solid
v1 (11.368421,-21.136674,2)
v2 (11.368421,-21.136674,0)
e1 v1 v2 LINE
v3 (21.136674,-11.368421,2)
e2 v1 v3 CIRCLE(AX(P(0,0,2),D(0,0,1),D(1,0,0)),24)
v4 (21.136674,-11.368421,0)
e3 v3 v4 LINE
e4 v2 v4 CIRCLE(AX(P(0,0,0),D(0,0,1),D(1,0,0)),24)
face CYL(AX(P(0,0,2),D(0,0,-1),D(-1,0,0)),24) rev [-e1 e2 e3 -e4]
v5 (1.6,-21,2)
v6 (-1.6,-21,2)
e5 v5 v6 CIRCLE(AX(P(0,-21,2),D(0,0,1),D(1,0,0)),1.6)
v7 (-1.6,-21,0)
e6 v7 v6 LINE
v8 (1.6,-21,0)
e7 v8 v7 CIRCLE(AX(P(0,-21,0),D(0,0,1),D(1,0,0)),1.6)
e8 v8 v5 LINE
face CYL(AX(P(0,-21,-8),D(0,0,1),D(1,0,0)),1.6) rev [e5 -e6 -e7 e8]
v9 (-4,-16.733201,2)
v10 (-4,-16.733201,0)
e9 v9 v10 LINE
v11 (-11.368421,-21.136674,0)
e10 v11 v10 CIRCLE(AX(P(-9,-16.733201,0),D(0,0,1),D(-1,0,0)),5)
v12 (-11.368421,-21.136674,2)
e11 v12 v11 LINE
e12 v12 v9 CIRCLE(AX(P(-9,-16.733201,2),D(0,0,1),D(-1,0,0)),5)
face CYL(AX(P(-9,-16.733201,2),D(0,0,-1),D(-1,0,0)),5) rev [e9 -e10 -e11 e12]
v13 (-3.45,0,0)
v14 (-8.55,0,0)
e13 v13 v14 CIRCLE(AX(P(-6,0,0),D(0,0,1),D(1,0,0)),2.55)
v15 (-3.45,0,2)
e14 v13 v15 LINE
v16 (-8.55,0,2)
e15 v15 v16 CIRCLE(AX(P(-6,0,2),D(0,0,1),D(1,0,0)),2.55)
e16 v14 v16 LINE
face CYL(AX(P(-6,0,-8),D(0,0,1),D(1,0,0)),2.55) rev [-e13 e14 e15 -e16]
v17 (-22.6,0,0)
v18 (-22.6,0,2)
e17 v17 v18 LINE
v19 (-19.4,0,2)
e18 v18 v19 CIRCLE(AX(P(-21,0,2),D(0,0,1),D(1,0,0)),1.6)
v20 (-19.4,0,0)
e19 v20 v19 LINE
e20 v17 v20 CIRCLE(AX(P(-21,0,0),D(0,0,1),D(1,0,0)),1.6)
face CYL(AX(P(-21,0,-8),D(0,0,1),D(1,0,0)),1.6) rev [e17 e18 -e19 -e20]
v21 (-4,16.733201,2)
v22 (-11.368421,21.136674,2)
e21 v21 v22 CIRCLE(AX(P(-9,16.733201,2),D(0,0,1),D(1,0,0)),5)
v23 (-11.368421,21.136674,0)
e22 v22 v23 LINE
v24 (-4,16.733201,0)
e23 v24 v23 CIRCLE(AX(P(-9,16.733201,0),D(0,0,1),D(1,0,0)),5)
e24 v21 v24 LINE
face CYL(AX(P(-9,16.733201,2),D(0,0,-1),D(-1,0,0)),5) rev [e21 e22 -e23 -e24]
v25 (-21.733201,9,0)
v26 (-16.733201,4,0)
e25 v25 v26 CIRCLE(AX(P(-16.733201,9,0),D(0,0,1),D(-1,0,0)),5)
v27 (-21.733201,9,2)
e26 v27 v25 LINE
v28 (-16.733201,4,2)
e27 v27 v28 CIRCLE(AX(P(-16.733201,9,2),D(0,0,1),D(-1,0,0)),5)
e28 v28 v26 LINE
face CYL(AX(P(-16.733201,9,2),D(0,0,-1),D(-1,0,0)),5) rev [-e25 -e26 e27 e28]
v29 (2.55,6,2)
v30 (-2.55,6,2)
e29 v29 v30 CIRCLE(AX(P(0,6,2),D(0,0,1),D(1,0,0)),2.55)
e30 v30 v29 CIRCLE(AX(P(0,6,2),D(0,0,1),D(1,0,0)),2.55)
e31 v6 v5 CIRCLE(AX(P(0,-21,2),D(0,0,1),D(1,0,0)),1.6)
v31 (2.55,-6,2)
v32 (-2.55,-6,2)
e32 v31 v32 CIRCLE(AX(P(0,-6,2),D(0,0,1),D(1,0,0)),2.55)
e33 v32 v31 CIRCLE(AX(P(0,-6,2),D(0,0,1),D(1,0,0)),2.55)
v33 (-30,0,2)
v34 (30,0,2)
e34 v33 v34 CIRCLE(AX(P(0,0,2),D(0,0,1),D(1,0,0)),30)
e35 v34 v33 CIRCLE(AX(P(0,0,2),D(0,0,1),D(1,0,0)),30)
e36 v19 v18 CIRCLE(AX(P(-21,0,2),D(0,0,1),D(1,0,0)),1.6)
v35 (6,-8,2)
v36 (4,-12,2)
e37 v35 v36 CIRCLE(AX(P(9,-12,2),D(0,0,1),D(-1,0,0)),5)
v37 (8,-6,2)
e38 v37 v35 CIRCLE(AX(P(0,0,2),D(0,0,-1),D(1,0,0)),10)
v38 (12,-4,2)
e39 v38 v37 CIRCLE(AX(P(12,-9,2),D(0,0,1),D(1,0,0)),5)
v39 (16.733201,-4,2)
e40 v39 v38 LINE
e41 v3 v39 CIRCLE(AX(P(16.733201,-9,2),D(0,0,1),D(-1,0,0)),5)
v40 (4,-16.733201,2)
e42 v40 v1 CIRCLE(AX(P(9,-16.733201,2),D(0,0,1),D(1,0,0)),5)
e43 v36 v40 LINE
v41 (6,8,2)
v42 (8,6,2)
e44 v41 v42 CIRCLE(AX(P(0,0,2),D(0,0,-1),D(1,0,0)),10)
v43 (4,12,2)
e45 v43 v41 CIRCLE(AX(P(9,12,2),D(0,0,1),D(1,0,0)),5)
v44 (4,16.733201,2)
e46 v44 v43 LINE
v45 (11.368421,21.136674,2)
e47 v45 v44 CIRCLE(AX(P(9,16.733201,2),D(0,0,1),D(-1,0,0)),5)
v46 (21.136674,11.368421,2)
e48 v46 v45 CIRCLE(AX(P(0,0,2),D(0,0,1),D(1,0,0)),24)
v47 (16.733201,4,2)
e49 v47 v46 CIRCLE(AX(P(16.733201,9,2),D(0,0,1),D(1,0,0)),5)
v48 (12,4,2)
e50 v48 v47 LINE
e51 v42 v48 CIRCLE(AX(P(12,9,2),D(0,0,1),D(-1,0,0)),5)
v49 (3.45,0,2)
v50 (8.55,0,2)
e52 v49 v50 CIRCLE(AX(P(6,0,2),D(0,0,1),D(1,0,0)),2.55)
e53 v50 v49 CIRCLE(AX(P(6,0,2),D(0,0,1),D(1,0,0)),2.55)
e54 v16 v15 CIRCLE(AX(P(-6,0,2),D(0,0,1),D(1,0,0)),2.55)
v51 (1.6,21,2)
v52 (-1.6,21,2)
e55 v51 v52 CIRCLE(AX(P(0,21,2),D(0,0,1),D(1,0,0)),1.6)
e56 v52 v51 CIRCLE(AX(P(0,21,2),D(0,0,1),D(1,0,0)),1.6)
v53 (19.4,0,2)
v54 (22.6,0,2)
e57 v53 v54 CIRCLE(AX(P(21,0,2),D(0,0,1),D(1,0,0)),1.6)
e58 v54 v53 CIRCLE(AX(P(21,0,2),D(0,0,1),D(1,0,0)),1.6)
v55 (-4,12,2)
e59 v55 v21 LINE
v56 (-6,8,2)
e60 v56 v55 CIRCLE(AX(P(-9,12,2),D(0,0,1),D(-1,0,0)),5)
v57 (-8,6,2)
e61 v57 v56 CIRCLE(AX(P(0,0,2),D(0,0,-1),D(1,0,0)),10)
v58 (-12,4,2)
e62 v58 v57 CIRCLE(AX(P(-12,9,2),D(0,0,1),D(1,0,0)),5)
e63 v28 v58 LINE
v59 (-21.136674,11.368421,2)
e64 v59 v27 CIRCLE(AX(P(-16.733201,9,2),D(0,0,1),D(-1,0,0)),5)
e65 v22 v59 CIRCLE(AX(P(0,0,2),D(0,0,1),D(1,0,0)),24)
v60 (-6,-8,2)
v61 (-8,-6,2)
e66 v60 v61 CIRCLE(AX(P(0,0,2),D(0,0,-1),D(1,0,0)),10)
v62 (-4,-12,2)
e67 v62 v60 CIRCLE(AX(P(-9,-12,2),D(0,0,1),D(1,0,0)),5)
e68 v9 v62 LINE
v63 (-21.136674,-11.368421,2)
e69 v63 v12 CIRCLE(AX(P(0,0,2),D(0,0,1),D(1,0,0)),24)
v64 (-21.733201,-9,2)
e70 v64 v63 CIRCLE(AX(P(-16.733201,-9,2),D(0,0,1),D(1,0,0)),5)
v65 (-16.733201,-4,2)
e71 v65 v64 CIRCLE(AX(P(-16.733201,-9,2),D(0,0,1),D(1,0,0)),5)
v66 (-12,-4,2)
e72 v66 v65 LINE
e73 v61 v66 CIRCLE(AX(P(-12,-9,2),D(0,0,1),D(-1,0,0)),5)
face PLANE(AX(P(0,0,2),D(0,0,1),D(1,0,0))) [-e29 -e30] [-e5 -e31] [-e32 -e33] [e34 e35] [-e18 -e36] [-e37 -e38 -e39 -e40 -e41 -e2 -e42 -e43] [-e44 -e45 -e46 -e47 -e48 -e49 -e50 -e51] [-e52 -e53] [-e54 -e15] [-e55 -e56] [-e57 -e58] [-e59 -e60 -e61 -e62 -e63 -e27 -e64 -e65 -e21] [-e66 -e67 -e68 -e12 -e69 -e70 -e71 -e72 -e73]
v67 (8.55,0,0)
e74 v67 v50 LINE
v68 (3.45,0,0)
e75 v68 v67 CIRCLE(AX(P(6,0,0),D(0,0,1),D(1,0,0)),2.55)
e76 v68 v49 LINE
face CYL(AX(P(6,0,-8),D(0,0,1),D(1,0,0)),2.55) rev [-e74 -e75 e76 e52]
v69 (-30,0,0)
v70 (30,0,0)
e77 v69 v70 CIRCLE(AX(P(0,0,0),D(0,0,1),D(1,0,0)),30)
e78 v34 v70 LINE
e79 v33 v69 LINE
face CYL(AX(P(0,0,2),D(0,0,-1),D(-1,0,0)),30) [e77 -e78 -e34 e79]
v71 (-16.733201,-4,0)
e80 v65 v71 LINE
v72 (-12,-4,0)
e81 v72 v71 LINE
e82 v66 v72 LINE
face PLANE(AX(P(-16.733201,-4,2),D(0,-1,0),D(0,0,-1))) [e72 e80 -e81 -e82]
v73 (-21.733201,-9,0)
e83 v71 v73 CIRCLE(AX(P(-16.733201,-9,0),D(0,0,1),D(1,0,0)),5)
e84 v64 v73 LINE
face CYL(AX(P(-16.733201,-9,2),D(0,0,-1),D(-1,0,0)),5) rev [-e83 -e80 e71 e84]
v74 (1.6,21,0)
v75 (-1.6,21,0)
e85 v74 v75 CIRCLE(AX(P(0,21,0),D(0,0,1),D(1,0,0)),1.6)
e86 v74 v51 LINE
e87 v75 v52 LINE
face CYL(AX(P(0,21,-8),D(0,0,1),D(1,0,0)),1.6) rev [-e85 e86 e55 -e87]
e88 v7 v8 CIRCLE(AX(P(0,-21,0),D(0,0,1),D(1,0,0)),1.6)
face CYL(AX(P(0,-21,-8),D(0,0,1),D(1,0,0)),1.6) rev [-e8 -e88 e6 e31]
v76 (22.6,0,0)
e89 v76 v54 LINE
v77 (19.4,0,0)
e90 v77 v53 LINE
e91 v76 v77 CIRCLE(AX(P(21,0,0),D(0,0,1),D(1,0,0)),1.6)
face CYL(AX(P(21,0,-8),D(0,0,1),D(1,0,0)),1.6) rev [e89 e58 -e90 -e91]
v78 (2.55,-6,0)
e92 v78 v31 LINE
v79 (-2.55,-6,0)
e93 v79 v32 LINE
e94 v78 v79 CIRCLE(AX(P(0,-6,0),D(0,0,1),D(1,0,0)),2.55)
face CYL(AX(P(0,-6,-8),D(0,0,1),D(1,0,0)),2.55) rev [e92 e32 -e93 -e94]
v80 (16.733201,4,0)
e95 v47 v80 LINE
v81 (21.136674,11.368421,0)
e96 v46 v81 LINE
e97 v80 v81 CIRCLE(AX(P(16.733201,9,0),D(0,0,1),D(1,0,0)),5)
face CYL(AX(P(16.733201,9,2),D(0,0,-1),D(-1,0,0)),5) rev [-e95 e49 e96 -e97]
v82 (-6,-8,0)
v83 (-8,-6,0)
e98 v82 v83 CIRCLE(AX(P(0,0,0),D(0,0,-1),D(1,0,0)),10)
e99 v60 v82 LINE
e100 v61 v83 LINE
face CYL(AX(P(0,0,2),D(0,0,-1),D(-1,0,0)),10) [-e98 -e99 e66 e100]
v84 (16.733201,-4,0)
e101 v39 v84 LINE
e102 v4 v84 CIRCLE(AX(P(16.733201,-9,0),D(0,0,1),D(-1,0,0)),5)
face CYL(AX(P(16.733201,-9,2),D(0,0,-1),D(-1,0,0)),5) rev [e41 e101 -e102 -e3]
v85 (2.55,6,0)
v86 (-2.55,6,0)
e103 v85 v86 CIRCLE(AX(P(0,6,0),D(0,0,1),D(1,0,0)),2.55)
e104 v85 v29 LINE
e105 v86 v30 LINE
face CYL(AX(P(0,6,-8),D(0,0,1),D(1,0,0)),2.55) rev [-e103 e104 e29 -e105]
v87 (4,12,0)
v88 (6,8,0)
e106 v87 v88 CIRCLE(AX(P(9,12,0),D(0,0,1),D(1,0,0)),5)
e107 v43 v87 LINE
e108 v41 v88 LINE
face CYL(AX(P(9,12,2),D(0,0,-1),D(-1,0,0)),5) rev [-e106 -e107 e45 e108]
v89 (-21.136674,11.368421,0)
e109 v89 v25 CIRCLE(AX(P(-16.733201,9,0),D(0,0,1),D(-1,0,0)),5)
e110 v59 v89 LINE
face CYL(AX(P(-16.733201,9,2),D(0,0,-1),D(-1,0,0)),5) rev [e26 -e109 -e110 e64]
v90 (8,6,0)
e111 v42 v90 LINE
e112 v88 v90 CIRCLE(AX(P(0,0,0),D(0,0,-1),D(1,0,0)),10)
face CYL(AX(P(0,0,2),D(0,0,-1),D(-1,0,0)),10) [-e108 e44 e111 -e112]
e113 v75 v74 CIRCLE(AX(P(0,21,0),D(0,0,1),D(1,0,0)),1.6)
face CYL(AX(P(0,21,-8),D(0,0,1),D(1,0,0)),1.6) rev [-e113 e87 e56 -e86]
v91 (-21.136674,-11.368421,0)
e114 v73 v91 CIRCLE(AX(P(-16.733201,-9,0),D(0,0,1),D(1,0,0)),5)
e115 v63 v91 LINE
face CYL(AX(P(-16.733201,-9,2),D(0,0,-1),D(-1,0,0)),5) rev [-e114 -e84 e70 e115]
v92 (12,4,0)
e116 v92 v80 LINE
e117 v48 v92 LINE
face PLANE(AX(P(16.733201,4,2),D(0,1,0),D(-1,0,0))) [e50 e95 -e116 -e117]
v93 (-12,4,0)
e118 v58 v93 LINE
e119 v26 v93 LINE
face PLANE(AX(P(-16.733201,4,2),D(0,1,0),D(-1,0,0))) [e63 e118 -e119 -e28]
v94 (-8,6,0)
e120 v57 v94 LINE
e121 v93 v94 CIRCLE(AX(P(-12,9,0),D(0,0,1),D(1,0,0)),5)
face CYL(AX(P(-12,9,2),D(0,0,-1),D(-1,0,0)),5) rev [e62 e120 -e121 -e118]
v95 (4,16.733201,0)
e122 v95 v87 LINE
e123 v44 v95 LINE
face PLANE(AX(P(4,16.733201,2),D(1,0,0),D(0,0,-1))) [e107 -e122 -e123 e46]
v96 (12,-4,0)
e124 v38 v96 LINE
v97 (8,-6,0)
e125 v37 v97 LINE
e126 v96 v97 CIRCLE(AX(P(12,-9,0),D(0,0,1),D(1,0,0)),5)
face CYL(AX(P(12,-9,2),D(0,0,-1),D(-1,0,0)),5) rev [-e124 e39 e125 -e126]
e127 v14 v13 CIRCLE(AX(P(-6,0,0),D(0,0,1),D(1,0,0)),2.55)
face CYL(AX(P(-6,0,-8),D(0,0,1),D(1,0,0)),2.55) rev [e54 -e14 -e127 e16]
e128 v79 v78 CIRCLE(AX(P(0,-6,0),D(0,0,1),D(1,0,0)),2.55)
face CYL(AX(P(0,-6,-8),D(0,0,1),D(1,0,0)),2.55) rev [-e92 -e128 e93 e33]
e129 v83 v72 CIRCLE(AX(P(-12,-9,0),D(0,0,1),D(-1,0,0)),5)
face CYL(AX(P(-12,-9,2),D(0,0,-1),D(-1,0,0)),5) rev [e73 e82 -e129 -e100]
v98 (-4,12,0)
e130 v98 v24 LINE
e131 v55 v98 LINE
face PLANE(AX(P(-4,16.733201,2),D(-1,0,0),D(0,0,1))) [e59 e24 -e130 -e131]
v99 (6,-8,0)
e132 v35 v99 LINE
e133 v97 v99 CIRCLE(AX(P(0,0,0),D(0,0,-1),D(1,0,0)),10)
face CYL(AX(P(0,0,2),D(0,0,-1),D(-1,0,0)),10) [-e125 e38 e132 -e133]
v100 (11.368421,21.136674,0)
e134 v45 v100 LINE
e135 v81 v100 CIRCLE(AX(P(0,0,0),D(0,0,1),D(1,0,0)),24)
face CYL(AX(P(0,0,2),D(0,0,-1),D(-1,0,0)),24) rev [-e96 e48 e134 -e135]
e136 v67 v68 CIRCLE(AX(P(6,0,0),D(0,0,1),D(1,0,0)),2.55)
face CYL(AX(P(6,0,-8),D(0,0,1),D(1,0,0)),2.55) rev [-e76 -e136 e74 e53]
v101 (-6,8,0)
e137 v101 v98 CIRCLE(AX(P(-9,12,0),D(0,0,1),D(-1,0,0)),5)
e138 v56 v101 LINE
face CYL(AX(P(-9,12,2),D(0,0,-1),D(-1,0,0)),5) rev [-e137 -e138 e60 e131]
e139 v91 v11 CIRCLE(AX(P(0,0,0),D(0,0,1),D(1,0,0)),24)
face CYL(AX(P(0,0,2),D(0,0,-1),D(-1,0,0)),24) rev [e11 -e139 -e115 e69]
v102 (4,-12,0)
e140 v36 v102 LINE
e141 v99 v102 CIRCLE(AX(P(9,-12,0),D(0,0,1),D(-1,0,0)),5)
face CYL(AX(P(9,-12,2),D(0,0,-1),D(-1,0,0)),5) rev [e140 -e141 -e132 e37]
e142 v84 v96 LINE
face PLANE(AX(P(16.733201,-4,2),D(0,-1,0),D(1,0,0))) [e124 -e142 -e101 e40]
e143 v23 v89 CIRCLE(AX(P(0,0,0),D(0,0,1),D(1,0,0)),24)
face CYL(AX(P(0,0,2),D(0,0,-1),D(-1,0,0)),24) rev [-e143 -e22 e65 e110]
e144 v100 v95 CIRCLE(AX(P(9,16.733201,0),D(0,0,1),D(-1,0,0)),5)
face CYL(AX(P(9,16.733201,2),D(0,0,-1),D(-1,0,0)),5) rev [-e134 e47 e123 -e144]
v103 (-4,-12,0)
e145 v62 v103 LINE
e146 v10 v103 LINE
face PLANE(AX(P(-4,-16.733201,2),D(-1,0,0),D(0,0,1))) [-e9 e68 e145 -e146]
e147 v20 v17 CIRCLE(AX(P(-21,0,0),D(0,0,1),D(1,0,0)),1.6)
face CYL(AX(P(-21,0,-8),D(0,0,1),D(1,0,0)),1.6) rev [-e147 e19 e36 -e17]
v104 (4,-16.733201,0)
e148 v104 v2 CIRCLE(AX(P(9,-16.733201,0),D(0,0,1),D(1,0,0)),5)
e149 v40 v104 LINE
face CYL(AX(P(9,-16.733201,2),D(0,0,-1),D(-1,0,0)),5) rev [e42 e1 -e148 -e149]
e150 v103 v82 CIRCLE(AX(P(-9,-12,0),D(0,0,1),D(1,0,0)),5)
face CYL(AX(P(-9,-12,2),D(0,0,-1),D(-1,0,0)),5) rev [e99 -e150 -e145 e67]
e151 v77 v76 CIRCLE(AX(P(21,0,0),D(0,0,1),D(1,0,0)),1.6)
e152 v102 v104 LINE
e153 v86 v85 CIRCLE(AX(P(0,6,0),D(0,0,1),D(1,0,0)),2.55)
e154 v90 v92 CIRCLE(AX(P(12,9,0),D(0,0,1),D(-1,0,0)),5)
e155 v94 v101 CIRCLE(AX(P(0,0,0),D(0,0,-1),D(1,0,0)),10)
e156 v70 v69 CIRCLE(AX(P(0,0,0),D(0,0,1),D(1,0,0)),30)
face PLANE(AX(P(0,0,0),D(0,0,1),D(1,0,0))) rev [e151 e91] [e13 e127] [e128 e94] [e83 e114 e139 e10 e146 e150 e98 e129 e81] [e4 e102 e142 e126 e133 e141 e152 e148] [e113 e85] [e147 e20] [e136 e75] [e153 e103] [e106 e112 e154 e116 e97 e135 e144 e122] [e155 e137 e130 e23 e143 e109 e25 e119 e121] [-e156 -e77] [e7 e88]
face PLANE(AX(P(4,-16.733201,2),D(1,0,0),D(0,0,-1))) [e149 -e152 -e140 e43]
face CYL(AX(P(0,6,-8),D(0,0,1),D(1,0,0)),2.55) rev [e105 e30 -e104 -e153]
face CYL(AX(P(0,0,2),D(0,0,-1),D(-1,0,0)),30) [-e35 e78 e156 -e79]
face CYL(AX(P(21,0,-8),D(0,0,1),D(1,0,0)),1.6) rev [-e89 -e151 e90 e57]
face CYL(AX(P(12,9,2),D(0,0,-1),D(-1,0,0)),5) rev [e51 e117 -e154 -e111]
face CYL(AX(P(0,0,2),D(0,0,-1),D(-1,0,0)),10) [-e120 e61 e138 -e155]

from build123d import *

# Parameters (mm, degrees)
SKETCH_1_R          = 30
EXTRUDE_1_DEPTH     = 2
SKETCH_2_R          = 1.6
CUT_EXTRUDE_1_DEPTH = 10
SKETCH_3_R          = 2.55
CUT_EXTRUDE_2_DEPTH = 10


with BuildPart() as part:
    # 草图1 → 凸台-拉伸1 (new body)
    with BuildSketch(Plane.XY):
        Circle(SKETCH_1_R)
        with BuildLine():
            Line((4, 16.733200531), (4, 12))
            ThreePointArc((4, 12), (4.527864045, 9.763932023), (6, 8))
            ThreePointArc((6, 8), (7.071067812, 7.071067812), (8, 6))
            ThreePointArc((8, 6), (9.763932023, 4.527864045), (12, 4))
            Line((12, 4), (16.733200531, 4))
            ThreePointArc((16.733200531, 4), (21.025175907, 6.43505412), (21.136674355, 11.368421053))
            ThreePointArc((21.136674355, 11.368421053), (16.970562748, 16.970562748), (11.368421053, 21.136674355))
            ThreePointArc((11.368421053, 21.136674355), (6.43505412, 21.025175907), (4, 16.733200531))
        make_face(mode=Mode.SUBTRACT)
        with BuildLine():
            Line((-4, 16.733200531), (-4, 12))
            ThreePointArc((-4, 12), (-4.527864045, 9.763932023), (-6, 8))
            ThreePointArc((-6, 8), (-7.071067812, 7.071067812), (-8, 6))
            ThreePointArc((-8, 6), (-9.763932023, 4.527864045), (-12, 4))
            Line((-12, 4), (-16.733200531, 4))
            ThreePointArc((-16.733200531, 4), (-21.025175907, 6.43505412), (-21.136674355, 11.368421053))
            ThreePointArc((-21.136674355, 11.368421053), (-16.970562748, 16.970562748), (-11.368421053, 21.136674355))
            ThreePointArc((-11.368421053, 21.136674355), (-6.43505412, 21.025175907), (-4, 16.733200531))
        make_face(mode=Mode.SUBTRACT)
        with BuildLine():
            Line((16.733200531, -4), (12, -4))
            ThreePointArc((12, -4), (9.763932023, -4.527864045), (8, -6))
            ThreePointArc((8, -6), (7.071067812, -7.071067812), (6, -8))
            ThreePointArc((6, -8), (4.527864045, -9.763932023), (4, -12))
            Line((4, -12), (4, -16.733200531))
            ThreePointArc((4, -16.733200531), (6.43505412, -21.025175907), (11.368421053, -21.136674355))
            ThreePointArc((11.368421053, -21.136674355), (16.970562748, -16.970562748), (21.136674355, -11.368421053))
            ThreePointArc((21.136674355, -11.368421053), (21.025175907, -6.43505412), (16.733200531, -4))
        make_face(mode=Mode.SUBTRACT)
        with BuildLine():
            Line((-4, -16.733200531), (-4, -12))
            ThreePointArc((-4, -12), (-4.527864045, -9.763932023), (-6, -8))
            ThreePointArc((-6, -8), (-7.071067812, -7.071067812), (-8, -6))
            ThreePointArc((-8, -6), (-9.763932023, -4.527864045), (-12, -4))
            Line((-12, -4), (-16.733200531, -4))
            ThreePointArc((-16.733200531, -4), (-21.025175907, -6.43505412), (-21.136674355, -11.368421053))
            ThreePointArc((-21.136674355, -11.368421053), (-16.970562748, -16.970562748), (-11.368421053, -21.136674355))
            ThreePointArc((-11.368421053, -21.136674355), (-6.43505412, -21.025175907), (-4, -16.733200531))
        make_face(mode=Mode.SUBTRACT)
    extrude(amount=EXTRUDE_1_DEPTH)

    # 草图2 → 切除-拉伸1 (cut)
    with BuildSketch(Plane.XY.offset(2)):
        with Locations((-21, 0)):
            Circle(SKETCH_2_R)
        with Locations((0, 21)):
            Circle(SKETCH_2_R)
        with Locations((21, 0)):
            Circle(SKETCH_2_R)
        with Locations((0, -21)):
            Circle(SKETCH_2_R)
    extrude(amount=-CUT_EXTRUDE_1_DEPTH, mode=Mode.SUBTRACT)

    # 草图3 → 切除-拉伸2 (cut)
    with BuildSketch(Plane.XY.offset(2)):
        with Locations((0, 6)):
            Circle(SKETCH_3_R)
        with Locations((-6, 0)):
            Circle(SKETCH_3_R)
        with Locations((6, 0)):
            Circle(SKETCH_3_R)
        with Locations((0, -6)):
            Circle(SKETCH_3_R)
    extrude(amount=-CUT_EXTRUDE_2_DEPTH, mode=Mode.SUBTRACT)


solid = part.part
